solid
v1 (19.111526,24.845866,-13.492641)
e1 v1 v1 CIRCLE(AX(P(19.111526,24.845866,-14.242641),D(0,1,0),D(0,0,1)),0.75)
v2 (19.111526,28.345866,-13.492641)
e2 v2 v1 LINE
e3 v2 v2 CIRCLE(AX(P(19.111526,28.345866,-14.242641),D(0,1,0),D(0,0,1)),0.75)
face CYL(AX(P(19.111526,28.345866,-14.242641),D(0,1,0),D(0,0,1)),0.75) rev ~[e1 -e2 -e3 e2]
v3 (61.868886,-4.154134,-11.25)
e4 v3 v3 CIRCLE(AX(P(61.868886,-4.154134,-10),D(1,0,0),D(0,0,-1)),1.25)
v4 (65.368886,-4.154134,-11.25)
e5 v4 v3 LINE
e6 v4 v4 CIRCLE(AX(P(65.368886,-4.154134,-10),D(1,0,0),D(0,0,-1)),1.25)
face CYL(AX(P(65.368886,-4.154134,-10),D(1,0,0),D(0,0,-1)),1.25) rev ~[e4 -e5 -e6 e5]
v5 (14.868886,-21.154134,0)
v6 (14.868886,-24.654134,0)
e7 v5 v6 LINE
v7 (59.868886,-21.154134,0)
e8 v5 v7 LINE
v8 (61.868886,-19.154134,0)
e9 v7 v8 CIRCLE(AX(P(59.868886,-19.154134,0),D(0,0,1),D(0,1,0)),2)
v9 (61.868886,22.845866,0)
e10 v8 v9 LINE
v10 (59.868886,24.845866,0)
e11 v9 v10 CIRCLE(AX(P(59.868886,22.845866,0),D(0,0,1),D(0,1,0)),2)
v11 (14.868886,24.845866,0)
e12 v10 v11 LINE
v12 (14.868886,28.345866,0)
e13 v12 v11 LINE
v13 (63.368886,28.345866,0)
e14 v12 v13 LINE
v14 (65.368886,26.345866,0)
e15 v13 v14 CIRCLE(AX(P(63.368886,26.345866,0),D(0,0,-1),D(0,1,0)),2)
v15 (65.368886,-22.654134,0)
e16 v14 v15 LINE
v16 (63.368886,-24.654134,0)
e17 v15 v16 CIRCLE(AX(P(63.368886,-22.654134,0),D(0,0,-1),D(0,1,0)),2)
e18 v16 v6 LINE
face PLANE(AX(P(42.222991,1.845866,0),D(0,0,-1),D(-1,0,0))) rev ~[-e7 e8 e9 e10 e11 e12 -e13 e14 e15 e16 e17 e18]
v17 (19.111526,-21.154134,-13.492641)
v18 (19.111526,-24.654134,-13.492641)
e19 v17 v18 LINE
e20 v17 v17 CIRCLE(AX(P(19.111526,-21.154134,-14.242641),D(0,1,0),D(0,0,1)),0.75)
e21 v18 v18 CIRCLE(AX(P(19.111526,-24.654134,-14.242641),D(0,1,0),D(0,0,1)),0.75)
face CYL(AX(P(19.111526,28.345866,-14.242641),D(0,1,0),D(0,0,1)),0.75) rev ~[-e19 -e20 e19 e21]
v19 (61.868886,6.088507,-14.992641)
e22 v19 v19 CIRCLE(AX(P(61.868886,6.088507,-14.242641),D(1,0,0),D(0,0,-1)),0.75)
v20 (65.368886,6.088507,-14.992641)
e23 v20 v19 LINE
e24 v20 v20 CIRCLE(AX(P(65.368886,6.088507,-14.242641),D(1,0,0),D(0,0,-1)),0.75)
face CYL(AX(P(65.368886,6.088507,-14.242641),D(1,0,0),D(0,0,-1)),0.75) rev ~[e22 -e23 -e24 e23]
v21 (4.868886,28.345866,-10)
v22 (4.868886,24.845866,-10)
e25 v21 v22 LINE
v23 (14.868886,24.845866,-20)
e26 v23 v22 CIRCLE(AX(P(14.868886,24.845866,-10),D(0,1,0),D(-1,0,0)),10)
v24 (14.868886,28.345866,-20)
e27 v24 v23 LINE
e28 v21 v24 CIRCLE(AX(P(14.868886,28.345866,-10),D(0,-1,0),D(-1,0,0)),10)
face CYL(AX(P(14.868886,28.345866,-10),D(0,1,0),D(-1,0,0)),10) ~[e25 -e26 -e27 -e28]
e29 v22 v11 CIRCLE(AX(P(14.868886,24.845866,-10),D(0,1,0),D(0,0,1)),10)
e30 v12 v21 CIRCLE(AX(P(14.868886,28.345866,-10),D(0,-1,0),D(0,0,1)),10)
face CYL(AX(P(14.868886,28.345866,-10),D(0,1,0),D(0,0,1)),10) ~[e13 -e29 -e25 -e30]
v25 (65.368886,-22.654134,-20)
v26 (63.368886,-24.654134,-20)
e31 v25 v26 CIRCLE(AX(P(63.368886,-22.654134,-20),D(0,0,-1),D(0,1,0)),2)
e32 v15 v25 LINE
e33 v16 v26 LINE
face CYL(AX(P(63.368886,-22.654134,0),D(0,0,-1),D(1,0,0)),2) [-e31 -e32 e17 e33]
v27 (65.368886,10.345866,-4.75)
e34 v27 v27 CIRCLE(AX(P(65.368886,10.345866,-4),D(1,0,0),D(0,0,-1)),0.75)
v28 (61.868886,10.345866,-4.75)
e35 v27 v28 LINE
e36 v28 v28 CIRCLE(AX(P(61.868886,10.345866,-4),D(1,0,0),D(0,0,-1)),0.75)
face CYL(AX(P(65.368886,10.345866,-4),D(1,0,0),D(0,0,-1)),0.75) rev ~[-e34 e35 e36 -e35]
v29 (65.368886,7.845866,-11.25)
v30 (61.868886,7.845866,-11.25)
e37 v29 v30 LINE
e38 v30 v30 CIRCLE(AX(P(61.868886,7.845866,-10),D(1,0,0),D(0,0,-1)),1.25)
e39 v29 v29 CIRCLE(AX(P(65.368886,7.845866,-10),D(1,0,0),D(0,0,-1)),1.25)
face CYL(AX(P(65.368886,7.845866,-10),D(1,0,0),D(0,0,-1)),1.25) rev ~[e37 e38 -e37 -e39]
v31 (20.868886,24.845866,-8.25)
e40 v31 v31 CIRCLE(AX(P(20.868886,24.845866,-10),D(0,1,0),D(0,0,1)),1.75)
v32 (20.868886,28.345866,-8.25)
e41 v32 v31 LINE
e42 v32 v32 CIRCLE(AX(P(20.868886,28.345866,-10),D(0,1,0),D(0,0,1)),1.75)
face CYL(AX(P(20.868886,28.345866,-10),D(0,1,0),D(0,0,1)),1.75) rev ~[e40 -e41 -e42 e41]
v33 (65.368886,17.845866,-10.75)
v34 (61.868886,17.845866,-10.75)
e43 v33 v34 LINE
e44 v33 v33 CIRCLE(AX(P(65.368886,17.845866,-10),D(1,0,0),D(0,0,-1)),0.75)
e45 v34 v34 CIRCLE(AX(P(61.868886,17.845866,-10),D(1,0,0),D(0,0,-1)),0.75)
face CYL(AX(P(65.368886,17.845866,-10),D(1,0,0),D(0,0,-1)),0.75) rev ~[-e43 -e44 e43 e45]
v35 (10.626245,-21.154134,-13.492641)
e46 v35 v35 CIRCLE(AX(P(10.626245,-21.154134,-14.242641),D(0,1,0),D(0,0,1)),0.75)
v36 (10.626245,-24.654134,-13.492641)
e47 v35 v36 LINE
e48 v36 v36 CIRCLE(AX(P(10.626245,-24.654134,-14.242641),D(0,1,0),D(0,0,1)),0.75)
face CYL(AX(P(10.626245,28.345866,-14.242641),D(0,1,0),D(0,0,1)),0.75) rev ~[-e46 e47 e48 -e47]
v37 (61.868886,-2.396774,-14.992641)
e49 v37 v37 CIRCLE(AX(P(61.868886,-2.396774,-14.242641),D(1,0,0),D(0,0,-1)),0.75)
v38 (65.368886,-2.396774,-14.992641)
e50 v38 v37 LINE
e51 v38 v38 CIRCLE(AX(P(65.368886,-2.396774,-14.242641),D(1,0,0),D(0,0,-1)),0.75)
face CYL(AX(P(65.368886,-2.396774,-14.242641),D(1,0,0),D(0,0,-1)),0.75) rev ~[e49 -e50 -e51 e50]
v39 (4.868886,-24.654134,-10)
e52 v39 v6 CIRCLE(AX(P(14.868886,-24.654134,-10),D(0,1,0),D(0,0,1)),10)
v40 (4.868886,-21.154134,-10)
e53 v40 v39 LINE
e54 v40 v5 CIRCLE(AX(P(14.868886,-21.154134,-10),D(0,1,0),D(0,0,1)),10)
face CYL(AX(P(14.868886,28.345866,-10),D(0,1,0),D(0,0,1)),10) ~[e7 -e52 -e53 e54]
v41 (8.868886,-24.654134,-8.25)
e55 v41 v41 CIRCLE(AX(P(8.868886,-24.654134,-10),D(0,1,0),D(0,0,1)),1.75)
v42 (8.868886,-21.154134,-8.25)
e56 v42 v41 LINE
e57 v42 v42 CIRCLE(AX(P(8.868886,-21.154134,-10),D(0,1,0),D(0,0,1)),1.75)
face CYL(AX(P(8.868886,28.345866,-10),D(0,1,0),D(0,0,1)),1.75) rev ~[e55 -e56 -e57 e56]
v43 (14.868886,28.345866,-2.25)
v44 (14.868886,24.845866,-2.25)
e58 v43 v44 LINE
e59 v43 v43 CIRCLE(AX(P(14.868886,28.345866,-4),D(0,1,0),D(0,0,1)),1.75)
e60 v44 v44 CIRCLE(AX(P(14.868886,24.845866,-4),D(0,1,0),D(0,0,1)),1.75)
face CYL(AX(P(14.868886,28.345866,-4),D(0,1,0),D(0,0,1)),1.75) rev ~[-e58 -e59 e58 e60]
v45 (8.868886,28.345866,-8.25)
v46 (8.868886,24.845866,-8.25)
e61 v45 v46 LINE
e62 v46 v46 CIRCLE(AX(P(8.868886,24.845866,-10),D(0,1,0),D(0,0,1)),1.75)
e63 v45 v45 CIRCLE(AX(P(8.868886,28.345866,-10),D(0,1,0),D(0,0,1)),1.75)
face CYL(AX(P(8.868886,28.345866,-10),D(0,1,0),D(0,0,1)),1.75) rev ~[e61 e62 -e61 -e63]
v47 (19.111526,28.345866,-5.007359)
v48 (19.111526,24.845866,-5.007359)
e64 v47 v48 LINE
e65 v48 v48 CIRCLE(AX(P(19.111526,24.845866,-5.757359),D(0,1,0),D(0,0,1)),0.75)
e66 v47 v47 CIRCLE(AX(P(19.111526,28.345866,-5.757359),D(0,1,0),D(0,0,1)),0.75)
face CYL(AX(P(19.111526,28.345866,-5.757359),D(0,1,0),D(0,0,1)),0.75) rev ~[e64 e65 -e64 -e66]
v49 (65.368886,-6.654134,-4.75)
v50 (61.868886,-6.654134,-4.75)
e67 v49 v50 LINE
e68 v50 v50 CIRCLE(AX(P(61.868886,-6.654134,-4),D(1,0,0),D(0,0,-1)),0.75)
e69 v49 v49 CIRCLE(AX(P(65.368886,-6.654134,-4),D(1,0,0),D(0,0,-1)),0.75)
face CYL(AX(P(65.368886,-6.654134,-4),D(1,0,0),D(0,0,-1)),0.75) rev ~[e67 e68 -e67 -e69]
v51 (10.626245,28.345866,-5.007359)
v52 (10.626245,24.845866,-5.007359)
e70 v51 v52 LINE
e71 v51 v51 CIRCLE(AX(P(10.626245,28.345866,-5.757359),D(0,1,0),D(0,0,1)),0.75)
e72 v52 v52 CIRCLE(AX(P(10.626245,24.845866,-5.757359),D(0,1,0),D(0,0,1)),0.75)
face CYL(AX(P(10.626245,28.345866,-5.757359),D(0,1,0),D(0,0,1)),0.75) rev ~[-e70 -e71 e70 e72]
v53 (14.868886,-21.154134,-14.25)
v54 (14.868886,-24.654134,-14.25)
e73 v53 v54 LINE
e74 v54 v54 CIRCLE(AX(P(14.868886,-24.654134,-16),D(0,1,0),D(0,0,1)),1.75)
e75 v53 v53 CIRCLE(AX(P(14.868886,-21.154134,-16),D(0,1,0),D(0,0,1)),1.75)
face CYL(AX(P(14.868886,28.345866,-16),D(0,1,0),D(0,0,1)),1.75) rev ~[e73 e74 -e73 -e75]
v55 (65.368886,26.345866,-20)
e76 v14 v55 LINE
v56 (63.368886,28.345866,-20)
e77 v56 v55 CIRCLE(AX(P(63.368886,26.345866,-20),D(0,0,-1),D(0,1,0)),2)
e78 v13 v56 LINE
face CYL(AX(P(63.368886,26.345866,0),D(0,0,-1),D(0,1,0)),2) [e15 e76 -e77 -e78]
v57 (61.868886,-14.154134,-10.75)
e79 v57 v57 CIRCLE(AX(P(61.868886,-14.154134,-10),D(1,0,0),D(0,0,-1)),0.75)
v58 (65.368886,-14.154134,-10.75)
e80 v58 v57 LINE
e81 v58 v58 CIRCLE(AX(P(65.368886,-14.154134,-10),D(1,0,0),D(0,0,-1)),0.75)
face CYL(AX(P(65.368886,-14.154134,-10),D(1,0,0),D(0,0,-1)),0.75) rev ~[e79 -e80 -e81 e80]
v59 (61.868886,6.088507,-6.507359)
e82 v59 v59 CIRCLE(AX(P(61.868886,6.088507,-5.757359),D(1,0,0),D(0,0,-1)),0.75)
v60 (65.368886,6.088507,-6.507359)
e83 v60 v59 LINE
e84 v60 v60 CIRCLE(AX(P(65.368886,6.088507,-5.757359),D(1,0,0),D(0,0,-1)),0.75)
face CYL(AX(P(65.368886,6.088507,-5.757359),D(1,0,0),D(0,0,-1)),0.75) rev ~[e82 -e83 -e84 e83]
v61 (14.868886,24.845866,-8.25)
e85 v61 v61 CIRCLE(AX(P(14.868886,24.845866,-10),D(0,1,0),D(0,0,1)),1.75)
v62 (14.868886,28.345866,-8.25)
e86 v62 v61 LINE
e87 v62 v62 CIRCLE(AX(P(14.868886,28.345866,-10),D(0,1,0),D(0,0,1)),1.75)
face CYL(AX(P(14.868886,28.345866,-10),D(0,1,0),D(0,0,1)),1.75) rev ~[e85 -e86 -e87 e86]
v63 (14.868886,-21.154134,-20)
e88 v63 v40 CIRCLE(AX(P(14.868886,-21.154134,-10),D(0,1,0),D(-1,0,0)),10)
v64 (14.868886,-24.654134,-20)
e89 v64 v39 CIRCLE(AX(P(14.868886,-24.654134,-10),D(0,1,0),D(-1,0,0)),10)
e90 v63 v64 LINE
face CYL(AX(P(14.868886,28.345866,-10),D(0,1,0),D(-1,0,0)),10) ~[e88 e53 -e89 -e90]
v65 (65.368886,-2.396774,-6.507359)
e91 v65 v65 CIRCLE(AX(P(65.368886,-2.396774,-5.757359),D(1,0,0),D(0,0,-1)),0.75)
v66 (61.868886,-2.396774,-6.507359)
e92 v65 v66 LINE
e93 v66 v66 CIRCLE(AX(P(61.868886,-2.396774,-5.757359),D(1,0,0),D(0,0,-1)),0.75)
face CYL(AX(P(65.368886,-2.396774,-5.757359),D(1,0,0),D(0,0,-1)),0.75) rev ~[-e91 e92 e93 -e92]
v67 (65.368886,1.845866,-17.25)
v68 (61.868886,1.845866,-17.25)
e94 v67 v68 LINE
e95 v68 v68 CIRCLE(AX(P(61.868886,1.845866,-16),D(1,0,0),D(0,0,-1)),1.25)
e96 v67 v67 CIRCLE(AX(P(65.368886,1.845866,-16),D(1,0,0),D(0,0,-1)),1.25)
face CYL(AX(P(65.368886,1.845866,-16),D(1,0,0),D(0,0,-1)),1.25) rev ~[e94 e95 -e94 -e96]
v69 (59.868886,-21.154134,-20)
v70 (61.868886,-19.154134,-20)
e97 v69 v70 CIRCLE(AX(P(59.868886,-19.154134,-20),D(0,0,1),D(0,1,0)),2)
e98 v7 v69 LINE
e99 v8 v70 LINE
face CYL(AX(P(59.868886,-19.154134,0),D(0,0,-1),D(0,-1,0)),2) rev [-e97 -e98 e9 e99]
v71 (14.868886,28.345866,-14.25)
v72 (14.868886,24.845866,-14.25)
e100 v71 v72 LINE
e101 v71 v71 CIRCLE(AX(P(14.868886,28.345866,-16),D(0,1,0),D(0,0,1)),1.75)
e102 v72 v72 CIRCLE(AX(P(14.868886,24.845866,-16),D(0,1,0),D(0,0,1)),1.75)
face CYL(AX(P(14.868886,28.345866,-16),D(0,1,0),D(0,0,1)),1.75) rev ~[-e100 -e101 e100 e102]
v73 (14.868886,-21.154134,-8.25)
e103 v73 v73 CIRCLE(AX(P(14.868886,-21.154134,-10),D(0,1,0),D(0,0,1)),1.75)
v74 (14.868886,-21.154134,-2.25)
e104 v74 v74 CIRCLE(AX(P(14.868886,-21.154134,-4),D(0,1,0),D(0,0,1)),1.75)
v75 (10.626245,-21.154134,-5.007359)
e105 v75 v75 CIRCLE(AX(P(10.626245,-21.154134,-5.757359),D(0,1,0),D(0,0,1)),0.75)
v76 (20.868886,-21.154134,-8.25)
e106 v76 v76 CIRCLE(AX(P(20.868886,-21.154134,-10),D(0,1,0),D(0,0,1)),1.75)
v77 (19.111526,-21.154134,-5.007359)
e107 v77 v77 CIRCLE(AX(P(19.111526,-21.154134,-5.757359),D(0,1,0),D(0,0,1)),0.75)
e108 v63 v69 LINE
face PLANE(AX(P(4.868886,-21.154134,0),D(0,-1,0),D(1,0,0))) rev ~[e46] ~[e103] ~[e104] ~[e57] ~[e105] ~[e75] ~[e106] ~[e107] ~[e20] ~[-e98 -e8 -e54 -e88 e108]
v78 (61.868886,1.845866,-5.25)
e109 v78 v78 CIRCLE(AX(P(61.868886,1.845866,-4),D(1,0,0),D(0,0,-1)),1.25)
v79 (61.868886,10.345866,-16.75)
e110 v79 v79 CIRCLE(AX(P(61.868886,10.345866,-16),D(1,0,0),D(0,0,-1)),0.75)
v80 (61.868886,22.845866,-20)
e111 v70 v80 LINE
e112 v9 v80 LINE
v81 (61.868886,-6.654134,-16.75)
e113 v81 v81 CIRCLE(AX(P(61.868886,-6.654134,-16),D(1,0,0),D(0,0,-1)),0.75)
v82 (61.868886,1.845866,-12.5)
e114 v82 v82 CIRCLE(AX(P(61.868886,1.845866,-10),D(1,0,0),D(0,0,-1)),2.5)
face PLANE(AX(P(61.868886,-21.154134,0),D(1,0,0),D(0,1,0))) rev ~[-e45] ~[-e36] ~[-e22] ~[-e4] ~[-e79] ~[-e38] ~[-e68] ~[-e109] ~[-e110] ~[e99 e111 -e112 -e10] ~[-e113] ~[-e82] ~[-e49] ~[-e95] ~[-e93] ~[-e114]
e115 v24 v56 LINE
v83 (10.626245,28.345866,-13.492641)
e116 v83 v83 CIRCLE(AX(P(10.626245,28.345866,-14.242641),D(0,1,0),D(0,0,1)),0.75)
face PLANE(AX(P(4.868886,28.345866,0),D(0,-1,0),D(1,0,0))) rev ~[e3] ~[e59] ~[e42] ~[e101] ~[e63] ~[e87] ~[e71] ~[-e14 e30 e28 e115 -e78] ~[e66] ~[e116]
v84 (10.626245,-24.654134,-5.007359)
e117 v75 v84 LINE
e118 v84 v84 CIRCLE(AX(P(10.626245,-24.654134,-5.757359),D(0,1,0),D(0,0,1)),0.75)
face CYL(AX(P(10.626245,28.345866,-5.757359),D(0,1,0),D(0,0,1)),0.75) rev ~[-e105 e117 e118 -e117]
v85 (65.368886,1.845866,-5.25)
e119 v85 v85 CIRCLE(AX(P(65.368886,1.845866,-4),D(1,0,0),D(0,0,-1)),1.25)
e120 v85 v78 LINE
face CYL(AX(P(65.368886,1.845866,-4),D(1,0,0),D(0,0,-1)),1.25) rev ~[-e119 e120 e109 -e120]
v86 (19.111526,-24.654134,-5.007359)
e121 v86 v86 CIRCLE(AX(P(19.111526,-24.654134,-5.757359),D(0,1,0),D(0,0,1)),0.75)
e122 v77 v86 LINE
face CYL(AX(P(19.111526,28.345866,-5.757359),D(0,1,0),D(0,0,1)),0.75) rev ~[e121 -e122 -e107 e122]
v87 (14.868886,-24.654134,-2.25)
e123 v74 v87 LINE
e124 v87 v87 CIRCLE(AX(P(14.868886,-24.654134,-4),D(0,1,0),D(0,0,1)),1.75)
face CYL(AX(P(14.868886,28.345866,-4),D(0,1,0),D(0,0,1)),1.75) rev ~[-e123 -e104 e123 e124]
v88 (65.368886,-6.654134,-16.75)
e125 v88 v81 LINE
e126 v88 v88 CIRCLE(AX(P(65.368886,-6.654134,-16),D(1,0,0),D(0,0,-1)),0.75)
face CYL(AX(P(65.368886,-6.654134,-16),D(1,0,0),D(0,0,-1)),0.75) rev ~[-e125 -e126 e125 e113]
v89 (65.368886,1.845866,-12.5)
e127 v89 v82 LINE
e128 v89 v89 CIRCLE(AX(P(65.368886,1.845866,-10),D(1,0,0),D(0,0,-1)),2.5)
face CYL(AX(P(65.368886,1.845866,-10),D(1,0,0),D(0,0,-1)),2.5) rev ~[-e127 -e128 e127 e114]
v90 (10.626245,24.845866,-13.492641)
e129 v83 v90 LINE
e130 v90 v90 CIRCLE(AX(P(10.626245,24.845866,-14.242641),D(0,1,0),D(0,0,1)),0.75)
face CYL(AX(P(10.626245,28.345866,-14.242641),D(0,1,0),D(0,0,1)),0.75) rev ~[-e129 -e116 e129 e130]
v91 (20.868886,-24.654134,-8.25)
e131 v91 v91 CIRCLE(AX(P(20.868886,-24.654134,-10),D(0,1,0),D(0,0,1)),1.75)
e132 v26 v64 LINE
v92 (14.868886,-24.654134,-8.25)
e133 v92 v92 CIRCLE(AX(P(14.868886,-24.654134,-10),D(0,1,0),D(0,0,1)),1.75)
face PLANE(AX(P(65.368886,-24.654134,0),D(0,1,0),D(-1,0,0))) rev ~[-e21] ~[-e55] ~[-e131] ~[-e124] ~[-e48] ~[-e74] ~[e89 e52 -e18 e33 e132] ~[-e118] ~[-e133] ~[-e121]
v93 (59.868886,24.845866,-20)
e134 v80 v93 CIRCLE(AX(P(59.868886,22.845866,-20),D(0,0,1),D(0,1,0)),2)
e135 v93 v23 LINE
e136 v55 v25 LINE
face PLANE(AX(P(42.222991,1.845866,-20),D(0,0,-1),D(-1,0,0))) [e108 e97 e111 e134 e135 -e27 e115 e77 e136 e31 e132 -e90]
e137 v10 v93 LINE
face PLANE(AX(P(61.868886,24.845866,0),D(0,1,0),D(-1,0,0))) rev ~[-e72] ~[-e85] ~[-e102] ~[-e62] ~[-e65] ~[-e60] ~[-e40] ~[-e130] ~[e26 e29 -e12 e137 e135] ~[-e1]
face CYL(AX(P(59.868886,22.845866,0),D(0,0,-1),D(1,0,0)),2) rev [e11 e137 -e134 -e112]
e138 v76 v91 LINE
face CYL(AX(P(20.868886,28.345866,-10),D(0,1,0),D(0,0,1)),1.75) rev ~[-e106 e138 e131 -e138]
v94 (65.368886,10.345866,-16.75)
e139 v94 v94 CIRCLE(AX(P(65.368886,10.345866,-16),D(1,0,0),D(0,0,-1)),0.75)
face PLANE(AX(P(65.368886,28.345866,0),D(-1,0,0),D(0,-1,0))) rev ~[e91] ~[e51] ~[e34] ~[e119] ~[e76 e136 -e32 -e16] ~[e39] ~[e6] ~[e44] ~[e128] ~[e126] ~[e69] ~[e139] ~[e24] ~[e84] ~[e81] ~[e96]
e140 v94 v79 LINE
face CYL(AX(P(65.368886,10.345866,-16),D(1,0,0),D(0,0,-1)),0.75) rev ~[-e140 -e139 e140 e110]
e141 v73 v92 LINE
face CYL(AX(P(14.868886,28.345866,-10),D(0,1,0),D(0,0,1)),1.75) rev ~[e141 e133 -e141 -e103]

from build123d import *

# Parameters (mm, degrees)
BOSS_EXTRUDE1_DEPTH = 20
CUT_EXTRUDE1_DEPTH  = 87.499082058
SKETCH5_R           = 1.75
SKETCH5_R_2         = 0.75
CUT_EXTRUDE2_DEPTH  = 87.499082058
FILLET1_R           = 2
SKETCH6_R           = 2.5
SKETCH6_R_2         = 1.25
SKETCH6_R_3         = 0.75
CUT_EXTRUDE3_DEPTH  = 20
SKETCH7_R           = 0.75
CUT_EXTRUDE4_DEPTH  = 20
SKETCH8_R           = 0.75
CUT_EXTRUDE5_DEPTH  = 20
FILLET2_R           = 2


with BuildPart() as part:
    # Sketch2 → Boss-Extrude1 (new body)
    with BuildSketch(Plane.XY):
        Polygon((4.868885541, 24.845866319), (4.868885541, 28.345866319), (65.368885541, 28.345866319), (65.368885541, -24.654133681), (4.868885541, -24.654133681), (4.868885541, -21.154133681), (61.868885541, -21.154133681), (61.868885541, 24.845866319), align=None)
    extrude(amount=-BOSS_EXTRUDE1_DEPTH)

    # Sketch3 → Cut-Extrude1 (cut, through all)
    with BuildSketch(Plane(origin=(0, 28.345866319, 0), x_dir=(1, 0, 0), z_dir=(0, 1, 0))):
        with BuildLine():
            ThreePointArc((14.868885541, 0), (7.79781773, 2.928932188), (4.868885541, 10))
            Line((4.868885541, 10), (4.868885541, 0))
            Line((4.868885541, 0), (14.868885541, 0))
        make_face()
        with BuildLine():
            ThreePointArc((4.868885541, 10), (7.79781773, 17.071067812), (14.868885541, 20))
            Line((14.868885541, 20), (4.868885541, 20))
            Line((4.868885541, 20), (4.868885541, 10))
        make_face()
    extrude(amount=-CUT_EXTRUDE1_DEPTH, mode=Mode.SUBTRACT)

    # Sketch5 → Cut-Extrude2 (cut, through all)
    with BuildSketch(Plane(origin=(0, 28.345866319, 0), x_dir=(1, 0, 0), z_dir=(0, 1, 0))):
        with Locations(Location((14.868885541, 10, 0), (0, 0, 270))):
            Circle(SKETCH5_R)
        with Locations(Location((20.868885541, 10, 0), (0, 0, 270))):
            Circle(SKETCH5_R)
        with Locations(Location((14.868885541, 4, 0), (0, 0, 270))):
            Circle(SKETCH5_R)
        with Locations(Location((8.868885541, 10, 0), (0, 0, 270))):
            Circle(SKETCH5_R)
        with Locations(Location((14.868885541, 16, 0), (0, 0, 270))):
            Circle(SKETCH5_R)
        with Locations(Location((19.111526229, 5.757359313, 0), (0, 0, 270))):
            Circle(SKETCH5_R_2)
        with Locations(Location((10.626244854, 5.757359313, 0), (0, 0, 270))):
            Circle(SKETCH5_R_2)
        with Locations(Location((10.626244854, 14.242640687, 0), (0, 0, 270))):
            Circle(SKETCH5_R_2)
        with Locations(Location((19.111526229, 14.242640687, 0), (0, 0, 270))):
            Circle(SKETCH5_R_2)
    extrude(amount=-CUT_EXTRUDE2_DEPTH, mode=Mode.SUBTRACT)

    # Fillet1
    fillet1_edges = [part.edges().sort_by_distance(p)[0] for p in [
        (65.368885541, 28.345866319, -10),
        (65.368885541, -24.654133681, -10),
    ]]
    fillet(fillet1_edges, radius=FILLET1_R)

    # Sketch6 → Cut-Extrude3 (cut)
    with BuildSketch(Plane(origin=(65.368885541, 0, 0), x_dir=(0, 0, -1), z_dir=(1, 0, 0))):
        with Locations((10, 1.845866319)):
            Circle(SKETCH6_R)
        with Locations((10, 7.845866319)):
            Circle(SKETCH6_R_2)
        with Locations((16, 1.845866319)):
            Circle(SKETCH6_R_2)
        with Locations((10, -4.154133681)):
            Circle(SKETCH6_R_2)
        with Locations((4, 1.845866319)):
            Circle(SKETCH6_R_2)
        with Locations((14.242640687, 6.088507006)):
            Circle(SKETCH6_R_3)
        with Locations((14.242640687, -2.396774369)):
            Circle(SKETCH6_R_3)
        with Locations((5.757359313, -2.396774369)):
            Circle(SKETCH6_R_3)
        with Locations((5.757359313, 6.088507006)):
            Circle(SKETCH6_R_3)
    extrude(amount=-CUT_EXTRUDE3_DEPTH, mode=Mode.SUBTRACT)

    # Sketch7 → Cut-Extrude4 (cut)
    with BuildSketch(Plane(origin=(65.368885541, 0, 0), x_dir=(0, 0, -1), z_dir=(1, 0, 0))):
        with Locations((16, 10.345866319)):
            Circle(SKETCH7_R)
        with Locations((4, 10.345866319)):
            Circle(SKETCH7_R)
        with Locations((4, -6.654133681)):
            Circle(SKETCH7_R)
        with Locations((16, -6.654133681)):
            Circle(SKETCH7_R)
    extrude(amount=-CUT_EXTRUDE4_DEPTH, mode=Mode.SUBTRACT)

    # Sketch8 → Cut-Extrude5 (cut)
    with BuildSketch(Plane(origin=(65.368885541, 0, 0), x_dir=(0, 0, -1), z_dir=(1, 0, 0))):
        with Locations((10, 17.845866319)):
            Circle(SKETCH8_R)
        with Locations((10, -14.154133681)):
            Circle(SKETCH8_R)
    extrude(amount=-CUT_EXTRUDE5_DEPTH, mode=Mode.SUBTRACT)

    # Fillet2
    fillet2_edges = [part.edges().sort_by_distance(p)[0] for p in [
        (61.868885541, -21.154133681, -10),
        (61.868885541, 24.845866319, -10),
    ]]
    fillet(fillet2_edges, radius=FILLET2_R)


solid = part.part
